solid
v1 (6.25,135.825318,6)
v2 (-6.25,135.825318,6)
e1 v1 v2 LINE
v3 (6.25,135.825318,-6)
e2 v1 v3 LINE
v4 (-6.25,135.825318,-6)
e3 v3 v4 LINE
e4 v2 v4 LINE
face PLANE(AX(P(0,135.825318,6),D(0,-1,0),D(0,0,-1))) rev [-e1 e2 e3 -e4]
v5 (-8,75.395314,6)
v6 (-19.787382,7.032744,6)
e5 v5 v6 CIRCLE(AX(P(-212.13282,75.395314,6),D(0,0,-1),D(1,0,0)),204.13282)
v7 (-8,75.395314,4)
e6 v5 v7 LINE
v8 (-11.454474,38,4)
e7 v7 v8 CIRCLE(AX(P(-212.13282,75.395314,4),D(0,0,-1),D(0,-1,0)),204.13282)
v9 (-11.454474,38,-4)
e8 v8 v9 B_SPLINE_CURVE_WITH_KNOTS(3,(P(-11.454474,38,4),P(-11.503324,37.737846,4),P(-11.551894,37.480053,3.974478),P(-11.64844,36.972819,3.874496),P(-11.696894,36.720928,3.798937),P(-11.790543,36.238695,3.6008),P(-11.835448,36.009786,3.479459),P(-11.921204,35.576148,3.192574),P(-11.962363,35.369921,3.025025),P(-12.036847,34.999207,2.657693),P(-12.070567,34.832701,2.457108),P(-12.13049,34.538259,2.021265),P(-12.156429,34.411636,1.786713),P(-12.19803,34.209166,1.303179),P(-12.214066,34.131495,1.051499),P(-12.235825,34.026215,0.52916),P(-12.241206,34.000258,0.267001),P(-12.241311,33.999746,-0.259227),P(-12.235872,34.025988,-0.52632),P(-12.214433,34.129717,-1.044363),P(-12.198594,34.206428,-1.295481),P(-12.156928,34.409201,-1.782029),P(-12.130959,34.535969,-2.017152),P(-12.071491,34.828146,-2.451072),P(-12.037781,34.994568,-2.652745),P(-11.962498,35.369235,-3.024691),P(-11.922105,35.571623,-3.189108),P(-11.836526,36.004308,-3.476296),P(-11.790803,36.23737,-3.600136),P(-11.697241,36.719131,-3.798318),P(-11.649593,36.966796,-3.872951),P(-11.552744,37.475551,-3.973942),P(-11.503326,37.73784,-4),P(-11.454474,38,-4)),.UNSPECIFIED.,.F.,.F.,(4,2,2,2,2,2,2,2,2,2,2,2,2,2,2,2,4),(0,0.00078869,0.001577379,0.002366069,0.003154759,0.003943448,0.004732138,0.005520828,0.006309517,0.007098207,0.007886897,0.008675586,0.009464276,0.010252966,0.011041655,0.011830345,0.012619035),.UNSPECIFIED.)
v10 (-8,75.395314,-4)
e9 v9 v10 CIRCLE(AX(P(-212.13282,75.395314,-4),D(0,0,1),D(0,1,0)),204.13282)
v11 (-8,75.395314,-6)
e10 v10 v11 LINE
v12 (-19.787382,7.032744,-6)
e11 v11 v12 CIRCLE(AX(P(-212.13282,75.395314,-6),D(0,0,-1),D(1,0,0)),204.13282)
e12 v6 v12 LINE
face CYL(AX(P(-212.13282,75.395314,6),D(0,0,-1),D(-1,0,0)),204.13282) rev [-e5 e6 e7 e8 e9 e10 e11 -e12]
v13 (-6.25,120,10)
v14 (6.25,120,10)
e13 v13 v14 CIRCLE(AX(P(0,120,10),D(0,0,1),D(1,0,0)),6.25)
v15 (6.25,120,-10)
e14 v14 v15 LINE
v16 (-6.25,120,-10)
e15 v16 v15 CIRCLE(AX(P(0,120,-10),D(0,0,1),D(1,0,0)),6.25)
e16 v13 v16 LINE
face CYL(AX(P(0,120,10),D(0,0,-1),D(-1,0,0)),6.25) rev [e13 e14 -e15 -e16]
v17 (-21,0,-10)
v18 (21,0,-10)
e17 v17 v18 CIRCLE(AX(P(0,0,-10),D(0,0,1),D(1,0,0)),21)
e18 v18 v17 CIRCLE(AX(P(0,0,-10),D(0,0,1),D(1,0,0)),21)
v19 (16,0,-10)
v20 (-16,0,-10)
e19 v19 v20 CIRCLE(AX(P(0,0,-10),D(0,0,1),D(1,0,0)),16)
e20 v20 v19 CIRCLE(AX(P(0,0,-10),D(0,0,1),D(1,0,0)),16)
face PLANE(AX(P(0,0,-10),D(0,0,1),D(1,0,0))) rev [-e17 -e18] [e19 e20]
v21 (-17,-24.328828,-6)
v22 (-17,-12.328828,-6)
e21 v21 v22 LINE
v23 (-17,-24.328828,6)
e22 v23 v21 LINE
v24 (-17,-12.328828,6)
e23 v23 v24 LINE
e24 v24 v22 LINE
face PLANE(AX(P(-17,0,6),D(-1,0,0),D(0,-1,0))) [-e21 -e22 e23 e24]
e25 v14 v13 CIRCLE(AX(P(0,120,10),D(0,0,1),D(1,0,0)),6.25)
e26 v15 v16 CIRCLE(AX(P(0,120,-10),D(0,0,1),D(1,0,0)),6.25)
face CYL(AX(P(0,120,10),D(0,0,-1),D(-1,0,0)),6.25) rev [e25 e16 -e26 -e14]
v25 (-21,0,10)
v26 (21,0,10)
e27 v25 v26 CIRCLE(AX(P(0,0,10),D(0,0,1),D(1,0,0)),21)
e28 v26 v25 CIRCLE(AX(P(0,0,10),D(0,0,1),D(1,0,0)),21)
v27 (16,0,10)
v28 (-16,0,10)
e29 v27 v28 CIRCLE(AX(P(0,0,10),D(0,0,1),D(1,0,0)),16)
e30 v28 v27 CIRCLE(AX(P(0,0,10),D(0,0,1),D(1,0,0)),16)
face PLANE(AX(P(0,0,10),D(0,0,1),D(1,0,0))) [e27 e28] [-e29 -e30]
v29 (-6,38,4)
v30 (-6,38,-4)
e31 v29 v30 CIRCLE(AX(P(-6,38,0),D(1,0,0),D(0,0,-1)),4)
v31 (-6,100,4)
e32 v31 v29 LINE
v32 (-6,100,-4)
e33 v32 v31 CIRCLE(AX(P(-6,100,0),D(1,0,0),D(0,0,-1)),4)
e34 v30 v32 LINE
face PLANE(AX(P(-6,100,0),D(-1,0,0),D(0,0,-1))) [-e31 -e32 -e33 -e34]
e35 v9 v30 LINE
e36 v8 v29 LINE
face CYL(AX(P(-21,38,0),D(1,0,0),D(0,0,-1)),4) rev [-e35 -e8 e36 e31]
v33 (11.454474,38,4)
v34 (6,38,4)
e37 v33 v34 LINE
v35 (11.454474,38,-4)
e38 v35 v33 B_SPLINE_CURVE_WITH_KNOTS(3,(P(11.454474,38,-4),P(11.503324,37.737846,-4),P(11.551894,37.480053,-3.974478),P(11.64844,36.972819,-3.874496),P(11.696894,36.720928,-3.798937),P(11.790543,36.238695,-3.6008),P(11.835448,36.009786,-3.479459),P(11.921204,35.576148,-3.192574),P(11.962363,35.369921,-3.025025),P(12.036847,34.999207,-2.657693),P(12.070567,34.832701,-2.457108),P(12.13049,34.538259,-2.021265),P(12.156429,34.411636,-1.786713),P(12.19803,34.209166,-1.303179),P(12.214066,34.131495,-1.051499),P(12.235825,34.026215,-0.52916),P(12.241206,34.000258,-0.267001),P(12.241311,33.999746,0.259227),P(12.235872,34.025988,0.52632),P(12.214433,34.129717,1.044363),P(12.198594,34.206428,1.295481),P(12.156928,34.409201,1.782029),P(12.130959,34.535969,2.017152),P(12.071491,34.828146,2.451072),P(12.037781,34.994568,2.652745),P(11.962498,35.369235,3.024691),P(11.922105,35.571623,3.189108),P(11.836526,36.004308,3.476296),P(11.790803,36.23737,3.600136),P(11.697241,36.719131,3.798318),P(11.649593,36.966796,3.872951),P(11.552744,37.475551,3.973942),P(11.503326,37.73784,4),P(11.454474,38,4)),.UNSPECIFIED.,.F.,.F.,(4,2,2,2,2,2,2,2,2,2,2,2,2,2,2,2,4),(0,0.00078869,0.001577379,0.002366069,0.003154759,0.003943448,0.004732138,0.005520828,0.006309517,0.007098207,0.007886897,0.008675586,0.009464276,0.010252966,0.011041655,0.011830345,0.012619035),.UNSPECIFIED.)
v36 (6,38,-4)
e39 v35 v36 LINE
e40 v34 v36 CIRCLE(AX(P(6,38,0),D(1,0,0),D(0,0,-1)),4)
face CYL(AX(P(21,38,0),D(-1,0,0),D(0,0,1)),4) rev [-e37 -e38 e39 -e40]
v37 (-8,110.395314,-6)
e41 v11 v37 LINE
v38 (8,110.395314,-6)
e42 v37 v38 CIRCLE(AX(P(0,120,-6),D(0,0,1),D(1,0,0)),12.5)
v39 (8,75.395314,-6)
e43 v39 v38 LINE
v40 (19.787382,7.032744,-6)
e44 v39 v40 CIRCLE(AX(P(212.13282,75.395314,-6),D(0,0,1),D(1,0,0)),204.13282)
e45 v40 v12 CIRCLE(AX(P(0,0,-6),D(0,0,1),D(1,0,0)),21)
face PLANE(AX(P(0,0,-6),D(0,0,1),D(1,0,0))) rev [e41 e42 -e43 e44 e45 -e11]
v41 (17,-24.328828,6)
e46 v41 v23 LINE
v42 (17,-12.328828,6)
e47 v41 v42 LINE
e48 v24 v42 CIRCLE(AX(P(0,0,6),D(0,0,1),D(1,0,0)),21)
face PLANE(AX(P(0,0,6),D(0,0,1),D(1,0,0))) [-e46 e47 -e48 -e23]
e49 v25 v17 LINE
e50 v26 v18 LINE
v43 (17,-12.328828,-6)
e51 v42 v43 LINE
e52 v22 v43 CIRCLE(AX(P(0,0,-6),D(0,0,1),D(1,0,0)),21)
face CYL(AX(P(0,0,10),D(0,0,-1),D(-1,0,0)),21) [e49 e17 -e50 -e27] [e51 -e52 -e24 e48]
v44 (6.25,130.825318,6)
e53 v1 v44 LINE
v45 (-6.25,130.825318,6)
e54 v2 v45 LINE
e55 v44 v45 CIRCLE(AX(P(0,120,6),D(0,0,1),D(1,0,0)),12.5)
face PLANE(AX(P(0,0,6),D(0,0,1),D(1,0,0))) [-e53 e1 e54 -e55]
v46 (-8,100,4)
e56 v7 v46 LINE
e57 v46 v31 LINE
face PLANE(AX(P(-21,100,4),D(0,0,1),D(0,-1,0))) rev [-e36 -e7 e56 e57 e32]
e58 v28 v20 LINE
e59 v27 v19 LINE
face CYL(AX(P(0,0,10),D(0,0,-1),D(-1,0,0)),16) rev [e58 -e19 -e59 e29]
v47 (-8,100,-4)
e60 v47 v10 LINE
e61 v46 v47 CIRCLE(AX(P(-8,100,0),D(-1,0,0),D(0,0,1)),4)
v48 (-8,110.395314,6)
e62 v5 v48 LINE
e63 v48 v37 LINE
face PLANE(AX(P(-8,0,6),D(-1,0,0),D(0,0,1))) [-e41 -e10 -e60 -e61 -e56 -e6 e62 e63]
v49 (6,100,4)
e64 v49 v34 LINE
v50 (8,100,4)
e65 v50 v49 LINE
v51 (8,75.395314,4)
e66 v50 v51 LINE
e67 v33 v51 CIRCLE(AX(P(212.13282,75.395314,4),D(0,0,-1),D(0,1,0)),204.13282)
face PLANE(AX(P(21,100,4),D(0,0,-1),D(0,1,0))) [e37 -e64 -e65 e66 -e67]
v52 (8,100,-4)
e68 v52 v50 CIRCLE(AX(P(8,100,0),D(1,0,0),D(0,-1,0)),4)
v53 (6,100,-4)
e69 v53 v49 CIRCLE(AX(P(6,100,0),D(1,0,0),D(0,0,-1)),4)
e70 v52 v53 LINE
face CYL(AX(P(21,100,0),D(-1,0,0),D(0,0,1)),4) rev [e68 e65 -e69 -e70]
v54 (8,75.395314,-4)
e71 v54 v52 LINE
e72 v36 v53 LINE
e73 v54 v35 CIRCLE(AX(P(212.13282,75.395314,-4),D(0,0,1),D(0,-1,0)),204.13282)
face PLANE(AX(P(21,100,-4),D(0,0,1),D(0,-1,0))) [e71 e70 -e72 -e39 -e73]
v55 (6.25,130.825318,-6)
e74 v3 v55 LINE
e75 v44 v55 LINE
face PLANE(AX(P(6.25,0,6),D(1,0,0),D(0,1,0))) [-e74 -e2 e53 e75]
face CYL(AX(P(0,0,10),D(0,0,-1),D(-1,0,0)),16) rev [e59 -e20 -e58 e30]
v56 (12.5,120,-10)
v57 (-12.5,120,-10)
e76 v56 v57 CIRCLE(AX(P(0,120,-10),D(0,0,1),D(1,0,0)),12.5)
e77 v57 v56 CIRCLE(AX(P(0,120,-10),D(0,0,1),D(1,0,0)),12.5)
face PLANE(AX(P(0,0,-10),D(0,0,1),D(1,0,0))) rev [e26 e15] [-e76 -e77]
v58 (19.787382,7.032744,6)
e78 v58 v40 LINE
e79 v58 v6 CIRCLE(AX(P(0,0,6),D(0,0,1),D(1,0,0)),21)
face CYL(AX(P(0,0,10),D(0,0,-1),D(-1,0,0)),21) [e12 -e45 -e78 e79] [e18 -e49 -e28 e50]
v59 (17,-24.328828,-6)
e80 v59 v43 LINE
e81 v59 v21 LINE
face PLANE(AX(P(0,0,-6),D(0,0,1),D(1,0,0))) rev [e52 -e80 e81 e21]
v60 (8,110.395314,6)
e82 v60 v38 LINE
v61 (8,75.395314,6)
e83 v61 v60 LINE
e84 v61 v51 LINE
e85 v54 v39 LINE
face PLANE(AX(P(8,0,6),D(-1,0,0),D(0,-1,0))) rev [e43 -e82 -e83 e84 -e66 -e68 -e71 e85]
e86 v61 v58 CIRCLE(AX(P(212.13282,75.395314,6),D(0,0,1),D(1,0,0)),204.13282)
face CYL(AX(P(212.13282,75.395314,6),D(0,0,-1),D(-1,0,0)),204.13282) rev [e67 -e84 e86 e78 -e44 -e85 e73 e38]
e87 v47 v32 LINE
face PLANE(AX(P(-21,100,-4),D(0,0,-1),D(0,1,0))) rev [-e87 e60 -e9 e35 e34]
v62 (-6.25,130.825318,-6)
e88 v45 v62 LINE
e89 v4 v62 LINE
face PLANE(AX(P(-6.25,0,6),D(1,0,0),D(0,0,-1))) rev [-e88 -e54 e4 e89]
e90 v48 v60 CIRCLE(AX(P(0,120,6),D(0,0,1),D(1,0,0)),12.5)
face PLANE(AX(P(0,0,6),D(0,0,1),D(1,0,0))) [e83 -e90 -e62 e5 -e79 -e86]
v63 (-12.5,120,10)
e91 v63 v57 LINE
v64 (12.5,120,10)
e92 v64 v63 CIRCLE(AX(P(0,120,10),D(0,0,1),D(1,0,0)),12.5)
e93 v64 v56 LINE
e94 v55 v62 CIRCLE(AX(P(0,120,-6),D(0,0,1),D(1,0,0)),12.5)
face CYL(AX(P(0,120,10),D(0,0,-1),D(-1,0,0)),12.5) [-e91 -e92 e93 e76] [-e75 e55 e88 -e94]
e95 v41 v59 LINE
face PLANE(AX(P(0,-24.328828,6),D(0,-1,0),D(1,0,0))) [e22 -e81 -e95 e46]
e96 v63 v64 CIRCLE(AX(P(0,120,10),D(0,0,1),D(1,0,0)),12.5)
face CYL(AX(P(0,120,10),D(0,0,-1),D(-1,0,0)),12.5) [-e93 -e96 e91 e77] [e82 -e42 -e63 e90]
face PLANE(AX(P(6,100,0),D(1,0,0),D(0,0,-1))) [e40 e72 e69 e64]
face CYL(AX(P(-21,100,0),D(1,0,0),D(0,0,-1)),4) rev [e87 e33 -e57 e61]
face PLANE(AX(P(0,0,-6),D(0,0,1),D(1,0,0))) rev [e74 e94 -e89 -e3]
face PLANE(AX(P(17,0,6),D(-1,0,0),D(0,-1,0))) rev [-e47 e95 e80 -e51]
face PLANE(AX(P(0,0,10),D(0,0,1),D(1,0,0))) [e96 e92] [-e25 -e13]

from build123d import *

# Parameters (mm, degrees)
ROD_PROFILE_SKETCH_R   = 12.5
ROD_PROFILE_SKETCH_R_2 = 6.25
ROD_BODY_DEPTH         = 10
ROD_PROFILE_SKETCH_R_3 = 21
ROD_PROFILE_SKETCH_R_4 = 16
ROD_BODY_2_DEPTH       = 10
EYE_BOSS_DEPTH         = 6
WEB_START              = 6
WEB_RECESS_CUT_DEPTH   = 132.802456026


with BuildPart() as part:
    # Rod Profile Sketch → Rod Body (new, symmetric)
    with BuildSketch(Plane.XY):
        with Locations((0, 120)):
            Circle(ROD_PROFILE_SKETCH_R)
        with Locations((0, 120)):
            Circle(ROD_PROFILE_SKETCH_R_2, mode=Mode.SUBTRACT)
    extrude(amount=ROD_BODY_DEPTH, both=True)



with BuildPart() as body_2:
    # Rod Profile Sketch → Rod Body 2 (new, symmetric)
    with BuildSketch(Plane.XY):
        Circle(ROD_PROFILE_SKETCH_R_3)
        Circle(ROD_PROFILE_SKETCH_R_4, mode=Mode.SUBTRACT)
    extrude(amount=ROD_BODY_2_DEPTH, both=True)


with BuildPart() as part_1:
    add(part.part)

    add(body_2.part)  # Eye Boss merges body 2
    # Sketch1_3 → Eye Boss (add, symmetric)
    with BuildSketch(Plane.XY):
        with BuildLine():
            Line((-8, 110.395313644), (-8, 75.395313644))
            ThreePointArc((-8, 75.395313644), (-10.96842855, 40.709642053), (-19.787382488, 7.032744434))
            ThreePointArc((-19.787382488, 7.032744434), (0, 21), (19.787382488, 7.032744434))
            ThreePointArc((19.787382488, 7.032744434), (10.96842855, 40.709642053), (8, 75.395313644))
            Line((8, 75.395313644), (8, 110.395313644))
            ThreePointArc((8, 110.395313644), (0, 107.5), (-8, 110.395313644))
        make_face()
        with BuildLine():
            Line((-6.25, 135.825317547), (-6.25, 130.825317547))
            ThreePointArc((-6.25, 130.825317547), (0, 132.5), (6.25, 130.825317547))
            Line((6.25, 130.825317547), (6.25, 135.825317547))
            Line((6.25, 135.825317547), (-6.25, 135.825317547))
        make_face()
        with BuildLine():
            ThreePointArc((17, -12.328828006), (0, -21), (-17, -12.328828006))
            Line((-17, -12.328828006), (-17, -24.328828006))
            Line((-17, -24.328828006), (17, -24.328828006))
            Line((17, -24.328828006), (17, -12.328828006))
        make_face()
    extrude(amount=EYE_BOSS_DEPTH, both=True)

    # Web Recess Sketch → Web Recess Cut (cut, through all)
    with BuildSketch(Plane(origin=(0, 0, 0), x_dir=(0, 0, -1), z_dir=(1, 0, 0)).offset(WEB_START)):
        with BuildLine():
            Line((4, 100), (4, 38))
            ThreePointArc((4, 38), (0, 34), (-4, 38))
            Line((-4, 38), (-4, 100))
            ThreePointArc((-4, 100), (0, 104), (4, 100))
        make_face()
    web_recess_cut = extrude(amount=WEB_RECESS_CUT_DEPTH, mode=Mode.SUBTRACT)

    # Web Recess Mirror: Web Recess Cut across plane
    add(web_recess_cut.mirror(Plane(origin=(0, 0, 0), x_dir=(0, 0, 1), z_dir=(1, 0, 0))), mode=Mode.SUBTRACT)


solid = part_1.part
